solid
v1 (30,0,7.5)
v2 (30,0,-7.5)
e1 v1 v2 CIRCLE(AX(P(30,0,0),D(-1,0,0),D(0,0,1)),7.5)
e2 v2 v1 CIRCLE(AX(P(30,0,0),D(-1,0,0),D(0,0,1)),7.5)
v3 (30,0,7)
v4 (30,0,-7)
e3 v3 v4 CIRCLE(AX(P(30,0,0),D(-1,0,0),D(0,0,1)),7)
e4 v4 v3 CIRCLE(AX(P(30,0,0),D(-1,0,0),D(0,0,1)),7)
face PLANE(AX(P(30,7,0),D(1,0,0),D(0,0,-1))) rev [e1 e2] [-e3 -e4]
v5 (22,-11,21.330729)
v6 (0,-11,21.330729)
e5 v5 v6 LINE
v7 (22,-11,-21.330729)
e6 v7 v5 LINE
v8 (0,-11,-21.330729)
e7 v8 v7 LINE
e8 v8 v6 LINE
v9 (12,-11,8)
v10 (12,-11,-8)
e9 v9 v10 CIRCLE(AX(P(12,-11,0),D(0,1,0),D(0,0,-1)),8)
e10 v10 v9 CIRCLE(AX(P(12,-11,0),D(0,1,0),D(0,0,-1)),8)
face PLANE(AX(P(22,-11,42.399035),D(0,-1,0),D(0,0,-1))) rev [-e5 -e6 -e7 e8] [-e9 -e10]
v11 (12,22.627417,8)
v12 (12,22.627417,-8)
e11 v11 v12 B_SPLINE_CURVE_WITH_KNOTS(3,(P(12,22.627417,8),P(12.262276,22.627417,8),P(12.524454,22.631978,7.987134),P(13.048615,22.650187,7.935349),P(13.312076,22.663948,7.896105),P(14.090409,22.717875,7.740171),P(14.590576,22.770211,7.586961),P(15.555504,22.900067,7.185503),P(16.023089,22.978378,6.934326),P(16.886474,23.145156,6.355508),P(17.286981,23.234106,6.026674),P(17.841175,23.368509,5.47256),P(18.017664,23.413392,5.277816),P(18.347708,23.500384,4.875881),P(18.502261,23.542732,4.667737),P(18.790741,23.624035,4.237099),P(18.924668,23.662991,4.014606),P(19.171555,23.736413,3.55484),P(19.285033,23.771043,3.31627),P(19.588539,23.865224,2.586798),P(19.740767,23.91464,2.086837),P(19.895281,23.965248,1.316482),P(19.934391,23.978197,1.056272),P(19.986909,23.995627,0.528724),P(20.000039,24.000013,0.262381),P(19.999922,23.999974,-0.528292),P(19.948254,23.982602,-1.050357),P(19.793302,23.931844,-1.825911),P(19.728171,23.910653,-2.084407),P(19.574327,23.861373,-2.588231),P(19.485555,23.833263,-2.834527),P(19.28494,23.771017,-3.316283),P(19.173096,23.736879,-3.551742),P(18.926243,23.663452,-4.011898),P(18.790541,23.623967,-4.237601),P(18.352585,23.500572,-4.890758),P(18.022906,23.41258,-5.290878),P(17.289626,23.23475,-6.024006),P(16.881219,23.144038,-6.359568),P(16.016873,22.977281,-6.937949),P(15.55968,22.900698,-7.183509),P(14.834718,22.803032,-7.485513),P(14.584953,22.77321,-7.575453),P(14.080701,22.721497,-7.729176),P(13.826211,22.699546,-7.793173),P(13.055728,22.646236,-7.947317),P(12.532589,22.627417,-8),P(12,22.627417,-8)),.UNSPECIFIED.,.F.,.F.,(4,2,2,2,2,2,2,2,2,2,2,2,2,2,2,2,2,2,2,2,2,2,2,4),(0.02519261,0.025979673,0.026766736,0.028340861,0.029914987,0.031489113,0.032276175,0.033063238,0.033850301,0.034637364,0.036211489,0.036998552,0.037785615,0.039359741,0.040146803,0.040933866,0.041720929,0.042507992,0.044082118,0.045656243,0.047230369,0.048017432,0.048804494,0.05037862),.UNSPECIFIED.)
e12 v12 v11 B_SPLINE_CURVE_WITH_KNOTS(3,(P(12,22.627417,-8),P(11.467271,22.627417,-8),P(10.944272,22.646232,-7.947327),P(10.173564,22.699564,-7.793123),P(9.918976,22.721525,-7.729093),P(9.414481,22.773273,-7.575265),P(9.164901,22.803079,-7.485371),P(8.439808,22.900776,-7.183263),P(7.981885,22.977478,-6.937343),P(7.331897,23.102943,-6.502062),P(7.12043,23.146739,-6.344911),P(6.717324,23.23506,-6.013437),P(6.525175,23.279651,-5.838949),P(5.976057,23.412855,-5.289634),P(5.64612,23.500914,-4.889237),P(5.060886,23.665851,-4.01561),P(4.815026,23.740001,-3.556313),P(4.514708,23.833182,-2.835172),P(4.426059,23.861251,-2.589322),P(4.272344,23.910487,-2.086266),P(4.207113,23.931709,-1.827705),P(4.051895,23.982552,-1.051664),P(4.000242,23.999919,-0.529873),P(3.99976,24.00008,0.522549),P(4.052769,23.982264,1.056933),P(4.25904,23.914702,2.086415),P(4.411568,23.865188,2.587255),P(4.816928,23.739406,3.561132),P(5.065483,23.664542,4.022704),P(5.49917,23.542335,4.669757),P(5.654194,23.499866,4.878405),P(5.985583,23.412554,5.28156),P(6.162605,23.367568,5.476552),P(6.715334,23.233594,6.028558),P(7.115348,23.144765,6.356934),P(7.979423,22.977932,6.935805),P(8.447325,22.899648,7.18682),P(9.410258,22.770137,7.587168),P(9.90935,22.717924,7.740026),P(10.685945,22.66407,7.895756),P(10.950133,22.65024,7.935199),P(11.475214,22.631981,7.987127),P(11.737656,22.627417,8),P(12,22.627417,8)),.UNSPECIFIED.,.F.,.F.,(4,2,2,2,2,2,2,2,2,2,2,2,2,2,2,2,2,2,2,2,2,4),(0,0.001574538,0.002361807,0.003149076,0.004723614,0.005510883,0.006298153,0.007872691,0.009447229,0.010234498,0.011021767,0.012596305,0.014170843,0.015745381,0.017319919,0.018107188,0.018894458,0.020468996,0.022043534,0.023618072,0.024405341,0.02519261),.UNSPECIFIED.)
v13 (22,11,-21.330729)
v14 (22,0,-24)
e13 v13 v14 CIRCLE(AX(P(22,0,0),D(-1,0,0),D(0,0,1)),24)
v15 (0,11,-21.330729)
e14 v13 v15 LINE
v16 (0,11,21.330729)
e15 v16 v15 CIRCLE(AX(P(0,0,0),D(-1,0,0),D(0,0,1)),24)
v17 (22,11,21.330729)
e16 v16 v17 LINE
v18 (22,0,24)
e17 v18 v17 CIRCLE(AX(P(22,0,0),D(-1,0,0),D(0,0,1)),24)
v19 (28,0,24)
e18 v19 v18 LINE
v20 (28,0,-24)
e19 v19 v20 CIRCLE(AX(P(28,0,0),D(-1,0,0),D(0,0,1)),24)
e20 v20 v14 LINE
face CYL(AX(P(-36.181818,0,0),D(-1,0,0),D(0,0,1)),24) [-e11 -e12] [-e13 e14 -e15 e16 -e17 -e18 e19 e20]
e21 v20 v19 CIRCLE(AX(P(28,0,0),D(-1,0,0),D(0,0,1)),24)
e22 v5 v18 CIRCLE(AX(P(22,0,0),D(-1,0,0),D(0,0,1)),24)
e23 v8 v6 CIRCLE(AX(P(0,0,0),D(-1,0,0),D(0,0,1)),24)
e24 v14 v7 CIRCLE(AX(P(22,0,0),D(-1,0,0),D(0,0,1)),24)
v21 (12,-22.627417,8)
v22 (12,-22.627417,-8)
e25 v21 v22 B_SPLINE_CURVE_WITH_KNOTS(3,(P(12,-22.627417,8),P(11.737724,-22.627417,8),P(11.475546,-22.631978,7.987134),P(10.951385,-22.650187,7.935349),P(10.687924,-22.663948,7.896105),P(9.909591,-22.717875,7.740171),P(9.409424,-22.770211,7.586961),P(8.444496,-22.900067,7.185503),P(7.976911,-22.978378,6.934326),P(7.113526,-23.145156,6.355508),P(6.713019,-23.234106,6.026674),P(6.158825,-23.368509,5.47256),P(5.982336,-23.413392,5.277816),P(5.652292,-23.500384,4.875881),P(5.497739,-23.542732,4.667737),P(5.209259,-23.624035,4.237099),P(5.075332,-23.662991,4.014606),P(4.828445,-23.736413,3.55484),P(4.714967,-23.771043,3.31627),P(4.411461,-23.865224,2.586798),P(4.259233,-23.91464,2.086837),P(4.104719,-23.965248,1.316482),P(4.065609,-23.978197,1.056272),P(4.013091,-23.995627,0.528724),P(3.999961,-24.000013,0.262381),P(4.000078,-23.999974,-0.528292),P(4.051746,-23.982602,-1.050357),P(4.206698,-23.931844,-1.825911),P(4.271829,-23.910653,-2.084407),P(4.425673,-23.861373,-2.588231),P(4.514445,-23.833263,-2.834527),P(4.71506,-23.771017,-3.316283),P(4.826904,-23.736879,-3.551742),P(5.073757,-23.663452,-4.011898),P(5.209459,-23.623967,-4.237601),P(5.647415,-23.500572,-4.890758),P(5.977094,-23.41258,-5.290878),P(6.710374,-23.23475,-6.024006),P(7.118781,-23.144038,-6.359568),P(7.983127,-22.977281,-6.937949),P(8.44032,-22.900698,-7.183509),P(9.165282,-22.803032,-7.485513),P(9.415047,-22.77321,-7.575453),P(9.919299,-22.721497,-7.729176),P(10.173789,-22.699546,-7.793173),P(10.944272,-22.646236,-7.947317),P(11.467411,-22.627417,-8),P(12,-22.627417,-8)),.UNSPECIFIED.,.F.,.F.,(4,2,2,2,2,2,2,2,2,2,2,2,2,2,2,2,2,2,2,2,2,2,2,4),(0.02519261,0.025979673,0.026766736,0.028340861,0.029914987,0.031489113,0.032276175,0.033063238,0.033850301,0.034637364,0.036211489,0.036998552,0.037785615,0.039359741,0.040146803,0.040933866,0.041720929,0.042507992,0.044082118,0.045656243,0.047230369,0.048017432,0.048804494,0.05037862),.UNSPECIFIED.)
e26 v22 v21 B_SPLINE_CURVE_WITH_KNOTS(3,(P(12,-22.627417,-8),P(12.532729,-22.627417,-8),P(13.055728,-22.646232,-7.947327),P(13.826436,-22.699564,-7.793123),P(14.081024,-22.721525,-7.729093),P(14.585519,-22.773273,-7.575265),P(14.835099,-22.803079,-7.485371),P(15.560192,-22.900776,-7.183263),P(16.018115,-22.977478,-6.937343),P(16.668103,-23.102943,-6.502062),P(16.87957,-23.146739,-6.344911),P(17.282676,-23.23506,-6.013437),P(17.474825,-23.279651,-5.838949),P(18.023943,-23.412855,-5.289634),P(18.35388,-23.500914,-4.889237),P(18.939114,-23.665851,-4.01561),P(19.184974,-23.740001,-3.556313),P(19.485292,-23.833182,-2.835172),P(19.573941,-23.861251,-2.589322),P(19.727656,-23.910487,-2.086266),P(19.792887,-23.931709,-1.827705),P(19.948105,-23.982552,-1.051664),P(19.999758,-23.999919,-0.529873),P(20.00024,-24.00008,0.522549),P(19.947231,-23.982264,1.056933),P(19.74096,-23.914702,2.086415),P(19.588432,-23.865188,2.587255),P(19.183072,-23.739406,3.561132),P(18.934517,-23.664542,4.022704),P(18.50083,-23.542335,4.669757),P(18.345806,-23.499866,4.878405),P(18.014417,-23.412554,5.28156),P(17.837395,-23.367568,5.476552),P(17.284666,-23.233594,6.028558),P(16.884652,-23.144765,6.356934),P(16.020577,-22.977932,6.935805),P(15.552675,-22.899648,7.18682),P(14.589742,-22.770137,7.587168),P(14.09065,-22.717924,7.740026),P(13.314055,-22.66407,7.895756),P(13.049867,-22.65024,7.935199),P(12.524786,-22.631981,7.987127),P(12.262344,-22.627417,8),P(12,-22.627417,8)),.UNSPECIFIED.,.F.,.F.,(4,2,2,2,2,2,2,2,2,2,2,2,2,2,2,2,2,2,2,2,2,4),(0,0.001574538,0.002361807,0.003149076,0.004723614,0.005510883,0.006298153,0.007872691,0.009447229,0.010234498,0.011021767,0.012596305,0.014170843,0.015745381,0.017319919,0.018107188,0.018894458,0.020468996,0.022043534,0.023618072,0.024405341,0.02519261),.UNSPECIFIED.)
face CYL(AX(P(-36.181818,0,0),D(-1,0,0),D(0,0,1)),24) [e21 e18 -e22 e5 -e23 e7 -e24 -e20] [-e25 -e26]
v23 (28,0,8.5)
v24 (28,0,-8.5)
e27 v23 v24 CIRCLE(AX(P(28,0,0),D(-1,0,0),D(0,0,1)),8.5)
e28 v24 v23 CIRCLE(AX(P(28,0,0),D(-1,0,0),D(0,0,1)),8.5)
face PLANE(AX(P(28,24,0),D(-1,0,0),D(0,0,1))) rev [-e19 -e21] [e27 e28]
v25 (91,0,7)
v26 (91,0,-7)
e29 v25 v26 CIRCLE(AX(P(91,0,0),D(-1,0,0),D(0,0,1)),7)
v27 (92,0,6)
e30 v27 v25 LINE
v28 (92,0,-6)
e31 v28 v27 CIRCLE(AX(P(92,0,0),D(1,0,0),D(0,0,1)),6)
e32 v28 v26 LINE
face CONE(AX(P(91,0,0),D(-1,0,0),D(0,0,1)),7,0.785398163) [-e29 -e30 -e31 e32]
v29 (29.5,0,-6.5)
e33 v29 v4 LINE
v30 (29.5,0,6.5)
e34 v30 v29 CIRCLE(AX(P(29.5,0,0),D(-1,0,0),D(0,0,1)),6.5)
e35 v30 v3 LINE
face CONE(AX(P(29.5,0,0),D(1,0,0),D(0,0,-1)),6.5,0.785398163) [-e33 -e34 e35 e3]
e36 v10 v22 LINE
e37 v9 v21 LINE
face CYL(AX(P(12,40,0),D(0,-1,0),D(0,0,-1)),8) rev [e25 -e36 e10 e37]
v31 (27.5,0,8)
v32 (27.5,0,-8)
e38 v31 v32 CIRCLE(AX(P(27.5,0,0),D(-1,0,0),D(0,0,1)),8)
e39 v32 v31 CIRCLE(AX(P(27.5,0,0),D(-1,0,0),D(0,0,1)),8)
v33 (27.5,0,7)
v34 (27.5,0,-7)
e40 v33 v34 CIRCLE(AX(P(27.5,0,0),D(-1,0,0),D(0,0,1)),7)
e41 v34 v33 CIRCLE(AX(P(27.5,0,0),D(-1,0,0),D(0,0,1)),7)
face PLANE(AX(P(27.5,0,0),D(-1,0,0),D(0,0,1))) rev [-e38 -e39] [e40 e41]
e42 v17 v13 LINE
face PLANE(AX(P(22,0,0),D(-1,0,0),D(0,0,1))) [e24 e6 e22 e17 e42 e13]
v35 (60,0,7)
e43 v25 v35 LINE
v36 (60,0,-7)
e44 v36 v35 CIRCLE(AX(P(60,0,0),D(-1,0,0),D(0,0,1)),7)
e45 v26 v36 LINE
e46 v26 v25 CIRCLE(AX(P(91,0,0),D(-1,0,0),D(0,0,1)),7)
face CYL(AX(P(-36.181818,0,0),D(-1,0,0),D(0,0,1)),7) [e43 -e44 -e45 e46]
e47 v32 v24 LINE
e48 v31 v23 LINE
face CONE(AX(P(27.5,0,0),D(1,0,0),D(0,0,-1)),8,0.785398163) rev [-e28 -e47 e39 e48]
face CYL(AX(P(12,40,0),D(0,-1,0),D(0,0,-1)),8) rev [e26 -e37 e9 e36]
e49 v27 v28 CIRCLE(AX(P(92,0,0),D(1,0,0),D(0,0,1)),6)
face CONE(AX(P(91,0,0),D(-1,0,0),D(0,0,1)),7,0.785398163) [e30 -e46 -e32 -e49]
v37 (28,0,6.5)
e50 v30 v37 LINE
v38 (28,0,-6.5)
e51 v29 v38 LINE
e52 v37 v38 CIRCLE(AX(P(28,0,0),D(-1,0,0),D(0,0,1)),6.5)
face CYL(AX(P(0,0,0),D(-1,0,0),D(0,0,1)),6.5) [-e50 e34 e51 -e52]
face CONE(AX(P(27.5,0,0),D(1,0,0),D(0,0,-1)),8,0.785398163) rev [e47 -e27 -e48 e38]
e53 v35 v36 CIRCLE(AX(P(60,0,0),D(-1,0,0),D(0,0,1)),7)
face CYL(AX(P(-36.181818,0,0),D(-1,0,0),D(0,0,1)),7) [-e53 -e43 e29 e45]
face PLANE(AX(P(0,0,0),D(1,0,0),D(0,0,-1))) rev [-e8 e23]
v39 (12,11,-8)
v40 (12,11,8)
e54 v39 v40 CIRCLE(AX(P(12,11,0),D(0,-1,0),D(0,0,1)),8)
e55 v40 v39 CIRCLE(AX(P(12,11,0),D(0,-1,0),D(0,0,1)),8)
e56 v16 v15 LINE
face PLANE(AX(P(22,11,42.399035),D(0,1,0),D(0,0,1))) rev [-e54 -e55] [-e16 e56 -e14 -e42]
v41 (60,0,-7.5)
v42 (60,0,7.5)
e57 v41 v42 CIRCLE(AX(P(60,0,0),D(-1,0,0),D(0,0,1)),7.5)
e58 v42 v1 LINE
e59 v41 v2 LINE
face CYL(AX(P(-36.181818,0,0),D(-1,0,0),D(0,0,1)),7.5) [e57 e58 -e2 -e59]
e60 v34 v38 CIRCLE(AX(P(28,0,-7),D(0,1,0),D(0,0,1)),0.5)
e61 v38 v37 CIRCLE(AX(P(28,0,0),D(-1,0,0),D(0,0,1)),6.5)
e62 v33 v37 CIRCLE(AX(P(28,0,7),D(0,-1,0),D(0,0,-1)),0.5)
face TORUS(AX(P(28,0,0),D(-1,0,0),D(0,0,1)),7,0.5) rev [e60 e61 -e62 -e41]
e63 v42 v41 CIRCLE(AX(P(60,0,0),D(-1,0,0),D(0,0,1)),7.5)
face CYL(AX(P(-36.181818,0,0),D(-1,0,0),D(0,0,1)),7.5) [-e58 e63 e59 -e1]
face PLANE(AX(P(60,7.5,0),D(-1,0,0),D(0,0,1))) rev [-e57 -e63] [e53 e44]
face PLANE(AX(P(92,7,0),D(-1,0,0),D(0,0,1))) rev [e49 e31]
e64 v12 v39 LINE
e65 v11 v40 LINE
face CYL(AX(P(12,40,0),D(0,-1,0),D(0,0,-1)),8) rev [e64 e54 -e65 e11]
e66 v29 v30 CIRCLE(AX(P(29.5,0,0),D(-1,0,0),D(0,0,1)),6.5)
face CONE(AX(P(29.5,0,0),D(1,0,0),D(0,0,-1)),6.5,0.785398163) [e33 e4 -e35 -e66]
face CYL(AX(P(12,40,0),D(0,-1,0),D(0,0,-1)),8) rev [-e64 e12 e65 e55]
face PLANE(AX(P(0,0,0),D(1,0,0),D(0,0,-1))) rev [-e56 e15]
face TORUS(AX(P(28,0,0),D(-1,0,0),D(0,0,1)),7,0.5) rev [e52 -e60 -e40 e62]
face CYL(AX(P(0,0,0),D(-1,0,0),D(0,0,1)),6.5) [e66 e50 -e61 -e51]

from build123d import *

# Parameters (mm, degrees)
SKETCH2_W               = 84.798069866
SKETCH2_H               = 22
CUT_EXTRUDE1_DEPTH      = 22
CUT_EXTRUDE2_DEPTH      = 51
CUT_EXTRUDE2_DEPTH_BACK = 22
SKETCH3_R               = 8
CHAMFER1_SIZE           = 1


with BuildPart() as part:
    # Sketch1 → Revolve1 (revolve)
    with BuildSketch(Plane.XY, mode=Mode.PRIVATE) as revolve1_sk:
        Polygon((0, 0), (0, 24), (28, 24), (28, 7), (30, 7), (30, 7.5), (60, 7.5), (60, 7), (92, 7), (92, 0), align=None)
    revolve(revolve1_sk.sketch.rotate(Axis((-36.181818182, 0, 0), (1, 0, 0)), 90), axis=Axis((-36.181818182, 0, 0), (1, 0, 0)))

    # Sketch2 → Cut-Extrude1 (cut)
    with BuildSketch(Plane.ZY):
        Rectangle(SKETCH2_W, SKETCH2_H)
    extrude(amount=-CUT_EXTRUDE1_DEPTH, mode=Mode.SUBTRACT)

    # Sketch3 → Cut-Extrude2 (cut, two sides: drawn at the far end of the back side and taken through both)
    with BuildSketch(Plane(origin=(0, -11, 0), x_dir=(1, 0, 0), z_dir=(0, 1, 0)).offset(-CUT_EXTRUDE2_DEPTH_BACK)):
        with Locations(Location((12, 0, 0), (0, 0, 90))):
            Circle(SKETCH3_R)
    extrude(amount=CUT_EXTRUDE2_DEPTH + CUT_EXTRUDE2_DEPTH_BACK, mode=Mode.SUBTRACT)

    # Sketch7 → Cut-Revolve1 (revolve, cut)
    with BuildSketch(Plane(origin=(0, 0, 0), x_dir=(1, 0, 0), z_dir=(0, 1, 0))):
        with BuildLine():
            Line((28, -6.5), (29.5, -6.5))
            Line((29.5, -6.5), (30, -7))
            Line((30, -7), (28, -7))
            Line((28, -7), (28, -8.5))
            Line((28, -8.5), (27.5, -8))
            Line((27.5, -8), (27.5, -7))
            ThreePointArc((27.5, -7), (27.646446609, -6.646446609), (28, -6.5))
        make_face()
    revolve(axis=Axis((0, 0, 0), (1, 0, 0)), mode=Mode.SUBTRACT)

    # Chamfer1
    chamfer1_edges = [part.edges().sort_by_distance(p)[0] for p in [
        (92, 0, -7),
    ]]
    chamfer(chamfer1_edges, length=CHAMFER1_SIZE)


solid = part.part
